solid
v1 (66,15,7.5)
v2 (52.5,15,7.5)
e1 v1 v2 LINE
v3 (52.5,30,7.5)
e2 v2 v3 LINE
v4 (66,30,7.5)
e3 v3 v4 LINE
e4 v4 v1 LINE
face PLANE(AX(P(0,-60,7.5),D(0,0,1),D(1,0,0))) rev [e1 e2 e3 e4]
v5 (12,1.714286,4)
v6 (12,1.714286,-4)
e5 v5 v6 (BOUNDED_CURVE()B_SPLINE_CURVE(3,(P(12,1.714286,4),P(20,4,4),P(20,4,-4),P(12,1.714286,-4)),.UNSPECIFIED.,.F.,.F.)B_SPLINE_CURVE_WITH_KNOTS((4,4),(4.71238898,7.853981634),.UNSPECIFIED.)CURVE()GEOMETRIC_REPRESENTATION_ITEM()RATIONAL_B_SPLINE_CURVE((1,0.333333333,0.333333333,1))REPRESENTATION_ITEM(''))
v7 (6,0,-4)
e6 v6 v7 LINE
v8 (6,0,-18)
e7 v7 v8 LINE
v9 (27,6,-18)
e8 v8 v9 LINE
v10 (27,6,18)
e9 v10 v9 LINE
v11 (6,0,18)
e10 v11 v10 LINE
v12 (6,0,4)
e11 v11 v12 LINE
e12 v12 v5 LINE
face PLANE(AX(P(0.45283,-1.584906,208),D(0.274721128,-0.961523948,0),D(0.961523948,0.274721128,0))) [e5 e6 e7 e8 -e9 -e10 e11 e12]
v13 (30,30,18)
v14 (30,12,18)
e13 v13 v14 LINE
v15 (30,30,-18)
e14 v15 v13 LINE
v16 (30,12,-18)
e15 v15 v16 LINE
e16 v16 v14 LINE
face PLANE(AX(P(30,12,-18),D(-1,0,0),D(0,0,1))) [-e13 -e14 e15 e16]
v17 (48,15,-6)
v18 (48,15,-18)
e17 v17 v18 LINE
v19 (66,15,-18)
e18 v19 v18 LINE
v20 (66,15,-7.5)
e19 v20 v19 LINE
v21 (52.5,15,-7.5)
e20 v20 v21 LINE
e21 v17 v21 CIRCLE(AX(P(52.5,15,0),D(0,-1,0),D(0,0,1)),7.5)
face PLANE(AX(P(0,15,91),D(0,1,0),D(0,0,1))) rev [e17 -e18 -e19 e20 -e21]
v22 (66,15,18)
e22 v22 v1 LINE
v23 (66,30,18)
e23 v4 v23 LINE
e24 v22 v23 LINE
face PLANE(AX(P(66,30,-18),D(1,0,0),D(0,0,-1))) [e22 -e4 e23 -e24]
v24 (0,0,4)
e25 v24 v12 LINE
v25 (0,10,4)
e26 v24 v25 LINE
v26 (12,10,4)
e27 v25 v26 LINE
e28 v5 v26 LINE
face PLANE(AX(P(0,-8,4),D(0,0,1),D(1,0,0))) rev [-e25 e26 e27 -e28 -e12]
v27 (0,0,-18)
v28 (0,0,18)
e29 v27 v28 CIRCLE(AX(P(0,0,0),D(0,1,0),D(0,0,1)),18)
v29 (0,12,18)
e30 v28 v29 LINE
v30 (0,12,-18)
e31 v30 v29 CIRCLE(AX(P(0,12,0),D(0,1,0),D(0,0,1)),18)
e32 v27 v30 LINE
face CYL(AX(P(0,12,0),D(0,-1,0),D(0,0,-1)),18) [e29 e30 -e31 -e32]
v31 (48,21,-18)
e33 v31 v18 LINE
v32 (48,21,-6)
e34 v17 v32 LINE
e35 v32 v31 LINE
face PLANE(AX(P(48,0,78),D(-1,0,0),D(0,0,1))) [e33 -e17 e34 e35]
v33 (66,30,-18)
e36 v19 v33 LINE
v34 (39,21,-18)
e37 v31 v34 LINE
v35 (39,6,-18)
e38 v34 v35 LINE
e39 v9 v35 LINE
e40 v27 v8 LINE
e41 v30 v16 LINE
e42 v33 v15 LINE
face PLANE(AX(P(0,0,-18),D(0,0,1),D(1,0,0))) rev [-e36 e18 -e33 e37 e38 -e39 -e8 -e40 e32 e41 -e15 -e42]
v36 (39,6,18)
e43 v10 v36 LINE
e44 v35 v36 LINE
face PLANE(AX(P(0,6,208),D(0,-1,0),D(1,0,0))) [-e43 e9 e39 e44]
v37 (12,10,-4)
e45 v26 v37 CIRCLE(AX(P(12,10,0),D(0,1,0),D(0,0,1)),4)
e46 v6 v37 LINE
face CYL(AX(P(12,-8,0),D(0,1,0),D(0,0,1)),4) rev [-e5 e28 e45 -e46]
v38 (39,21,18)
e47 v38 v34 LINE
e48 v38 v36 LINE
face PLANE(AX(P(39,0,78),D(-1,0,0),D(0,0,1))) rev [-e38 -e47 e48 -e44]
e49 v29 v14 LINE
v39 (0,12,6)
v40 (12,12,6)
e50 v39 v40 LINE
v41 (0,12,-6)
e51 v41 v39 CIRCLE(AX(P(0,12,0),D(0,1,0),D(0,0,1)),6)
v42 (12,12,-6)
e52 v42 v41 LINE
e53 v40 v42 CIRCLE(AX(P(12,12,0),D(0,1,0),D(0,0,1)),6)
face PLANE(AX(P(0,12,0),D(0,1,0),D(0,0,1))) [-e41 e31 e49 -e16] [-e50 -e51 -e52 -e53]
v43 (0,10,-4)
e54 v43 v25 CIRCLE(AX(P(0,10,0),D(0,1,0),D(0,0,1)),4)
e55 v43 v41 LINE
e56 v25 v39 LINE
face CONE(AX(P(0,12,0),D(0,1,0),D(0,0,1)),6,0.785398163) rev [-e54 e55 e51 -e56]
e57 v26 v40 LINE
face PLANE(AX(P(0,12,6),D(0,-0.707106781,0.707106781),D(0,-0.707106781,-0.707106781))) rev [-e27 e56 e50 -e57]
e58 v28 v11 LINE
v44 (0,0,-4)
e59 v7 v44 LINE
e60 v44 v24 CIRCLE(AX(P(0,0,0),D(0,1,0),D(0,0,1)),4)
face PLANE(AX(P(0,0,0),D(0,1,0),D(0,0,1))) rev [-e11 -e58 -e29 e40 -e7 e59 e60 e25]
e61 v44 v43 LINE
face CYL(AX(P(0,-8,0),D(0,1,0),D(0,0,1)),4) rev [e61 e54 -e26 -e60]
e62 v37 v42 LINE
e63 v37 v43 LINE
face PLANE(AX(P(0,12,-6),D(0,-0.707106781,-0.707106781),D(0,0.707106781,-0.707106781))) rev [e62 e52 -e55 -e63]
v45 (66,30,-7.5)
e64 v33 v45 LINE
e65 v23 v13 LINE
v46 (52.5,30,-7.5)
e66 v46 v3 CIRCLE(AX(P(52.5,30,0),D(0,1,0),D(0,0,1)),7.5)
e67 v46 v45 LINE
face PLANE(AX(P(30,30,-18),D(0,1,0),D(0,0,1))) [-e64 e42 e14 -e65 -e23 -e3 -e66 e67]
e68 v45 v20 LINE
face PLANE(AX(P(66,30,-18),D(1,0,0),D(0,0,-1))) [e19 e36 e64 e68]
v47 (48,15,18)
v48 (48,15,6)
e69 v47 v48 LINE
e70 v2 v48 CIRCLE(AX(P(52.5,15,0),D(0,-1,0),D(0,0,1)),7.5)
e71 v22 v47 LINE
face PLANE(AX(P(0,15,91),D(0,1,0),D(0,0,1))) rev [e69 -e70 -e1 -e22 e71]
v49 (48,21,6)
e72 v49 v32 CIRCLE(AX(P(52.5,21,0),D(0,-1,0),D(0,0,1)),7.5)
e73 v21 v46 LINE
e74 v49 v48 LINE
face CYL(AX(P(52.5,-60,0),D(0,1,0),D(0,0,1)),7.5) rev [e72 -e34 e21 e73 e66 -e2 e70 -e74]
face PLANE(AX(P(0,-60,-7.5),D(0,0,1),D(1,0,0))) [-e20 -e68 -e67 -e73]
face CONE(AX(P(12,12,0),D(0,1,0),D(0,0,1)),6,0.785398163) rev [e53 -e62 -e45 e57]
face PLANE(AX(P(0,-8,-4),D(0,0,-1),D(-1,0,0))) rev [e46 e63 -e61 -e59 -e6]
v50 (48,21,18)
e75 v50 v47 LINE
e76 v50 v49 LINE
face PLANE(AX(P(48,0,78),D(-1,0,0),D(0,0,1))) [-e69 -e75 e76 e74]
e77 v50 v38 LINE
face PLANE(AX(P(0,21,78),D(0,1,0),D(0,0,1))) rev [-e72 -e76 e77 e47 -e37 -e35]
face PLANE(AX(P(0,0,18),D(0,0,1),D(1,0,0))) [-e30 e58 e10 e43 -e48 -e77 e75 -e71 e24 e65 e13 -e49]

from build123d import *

# Parameters (mm, degrees)
HUB_SKETCH_R                = 18
HUB_36_DEPTH                = 12
ARM_START                   = -12
ARM_DEPTH                   = 12
HUB_SLOT_CHAMFER_45_DEPTH   = 2
HUB_SLOT_CHAMFER_45_DRAFT   = -45
HUB_SLOT_DEPTH              = 18
CLEVIS_BLOCK_DEPTH          = 36
CLEVIS_U_SLOT_SKETCH_W      = 13.5
CLEVIS_U_SLOT_SKETCH_H      = 15
CLEVIS_U_SLOT_DEPTH         = 90
BLOCK_STEP_CUT_DEPTH        = 60
BLOCK_STEP_CUT_DEPTH_BACK   = 147
BLOCK_STEP_CUT_SKETCH_W     = 9
BLOCK_STEP_CUT_SKETCH_H     = 21
ARM_TAPER_CUT_DEPTH         = 73
ARM_TAPER_CUT_DEPTH_BACK    = 190
ARM_TAPER_CUT_SKETCH_W      = 18
ARM_TAPER_CUT_SKETCH_H      = 15
BLOCK_RELIEF_CUT_DEPTH      = 190
BLOCK_RELIEF_CUT_DEPTH_BACK = 190


with BuildPart() as part:
    # Hub Sketch → Hub _36 (new body)
    with BuildSketch(Plane(origin=(0, 0, 0), x_dir=(1, 0, 0), z_dir=(0, 1, 0))):
        with Locations(Location((0, 0, 0), (0, 0, 270))):
            Circle(HUB_SKETCH_R)
    extrude(amount=HUB_36_DEPTH)

    # Arm Sketch → Arm (add)
    with BuildSketch(Plane(origin=(0, 12, 0), x_dir=(1, 0, 0), z_dir=(0, 1, 0)).offset(ARM_START)):
        with BuildLine():
            Line((30, 0), (18, 0))
            ThreePointArc((18, 0), (12.727922061, -12.727922061), (0, -18))
            Line((0, -18), (30, -18))
            Line((30, -18), (30, 0))
        make_face()
        with BuildLine():
            ThreePointArc((0, 18), (12.727922061, 12.727922061), (18, 0))
            Line((18, 0), (30, 0))
            Line((30, 0), (30, 18))
            Line((30, 18), (0, 18))
        make_face()
    extrude(amount=ARM_DEPTH)


with BuildPart() as hub_slot_chamfer_45_tool:
    # Hub Slot Chamfer Sketch → Hub Slot Chamfer 45 (with draft: the straight prism first)
    with BuildSketch(Plane(origin=(0, 12, 0), x_dir=(1, 0, 0), z_dir=(0, 1, 0))):
        with BuildLine():
            ThreePointArc((0, 6), (-6, 0), (0, -6))
            Line((0, -6), (12, -6))
            ThreePointArc((12, -6), (18, 0), (12, 6))
            Line((12, 6), (0, 6))
        make_face()
    extrude(amount=-HUB_SLOT_CHAMFER_45_DEPTH)
    # Hub Slot Chamfer 45: the draft: its side faces are tilted about the plane it starts from
    hub_slot_chamfer_45_sides = [hub_slot_chamfer_45_tool.faces().sort_by_distance(p)[0] for p in [
        (6, 11, -6),
        (-6, 11, 0),
        (6, 11, 6),
        (18, 11, 0),
    ]]
    draft(hub_slot_chamfer_45_sides, Plane(origin=(0, 12, 0), x_dir=(1, 0, 0), z_dir=(0, 1, 0)), HUB_SLOT_CHAMFER_45_DRAFT)


with BuildPart() as part_1:
    add(part.part)

    # Hub Slot Chamfer 45: cut by hub_slot_chamfer_45_tool
    add(hub_slot_chamfer_45_tool.part, mode=Mode.SUBTRACT)

    # Hub Slot Sketch → Hub Slot (cut)
    with BuildSketch(Plane(origin=(0, 10, 0), x_dir=(1, 0, 0), z_dir=(0, 1, 0))):
        with BuildLine():
            Line((12, 4), (0, 4))
            ThreePointArc((0, 4), (2.828427125, 2.828427125), (4, 0))
            ThreePointArc((4, 0), (2.828427125, -2.828427125), (0, -4))
            Line((0, -4), (12, -4))
            ThreePointArc((12, -4), (8, 0), (12, 4))
        make_face()
        with BuildLine():
            ThreePointArc((4, 0), (2.828427125, 2.828427125), (0, 4))
            ThreePointArc((0, 4), (-4, 0), (0, -4))
            ThreePointArc((0, -4), (2.828427125, -2.828427125), (4, 0))
        make_face()
        with BuildLine():
            ThreePointArc((16, 0), (14.828427125, 2.828427125), (12, 4))
            ThreePointArc((12, 4), (8, 0), (12, -4))
            ThreePointArc((12, -4), (14.828427125, -2.828427125), (16, 0))
        make_face()
    extrude(amount=-HUB_SLOT_DEPTH, mode=Mode.SUBTRACT)

    # Clevis Block Sketch → Clevis Block (add)
    with BuildSketch(Plane.XY.offset(18)):
        Polygon((30, 12), (30, 30), (66, 30), (66, 15), (66, 0), (30, 0), align=None)
    extrude(amount=-CLEVIS_BLOCK_DEPTH)

    # Clevis U-Slot Sketch → Clevis U-Slot (cut)
    with BuildSketch(Plane(origin=(0, 30, 0), x_dir=(1, 0, 0), z_dir=(0, 1, 0))):
        with BuildLine():
            Line((52.5, -7.5), (52.5, 7.5))
            ThreePointArc((52.5, 7.5), (45, 0), (52.5, -7.5))
        make_face()
        with Locations((59.25, 0)):
            Rectangle(CLEVIS_U_SLOT_SKETCH_W, CLEVIS_U_SLOT_SKETCH_H)
    extrude(amount=-CLEVIS_U_SLOT_DEPTH, mode=Mode.SUBTRACT)

    # Block Step Cut Sketch → Block Step Cut (cut, two sides: drawn at the far end of the back side and taken through both)
    with BuildSketch(Plane.XY.offset(18).offset(-BLOCK_STEP_CUT_DEPTH_BACK)):
        with Locations((43.5, 10.5)):
            Rectangle(BLOCK_STEP_CUT_SKETCH_W, BLOCK_STEP_CUT_SKETCH_H)
    extrude(amount=BLOCK_STEP_CUT_DEPTH + BLOCK_STEP_CUT_DEPTH_BACK, mode=Mode.SUBTRACT)

    # Arm Taper Cut Sketch → Arm Taper Cut (cut, two sides: drawn at the far end of the back side and taken through both)
    with BuildSketch(Plane.XY.offset(18).offset(-ARM_TAPER_CUT_DEPTH_BACK)):
        with Locations((57, 7.5)):
            Rectangle(ARM_TAPER_CUT_SKETCH_W, ARM_TAPER_CUT_SKETCH_H)
    extrude(amount=ARM_TAPER_CUT_DEPTH + ARM_TAPER_CUT_DEPTH_BACK, mode=Mode.SUBTRACT)

    # Block Relief Cut Sketch → Block Relief Cut (cut, two sides: drawn at the far end of the back side and taken through both)
    with BuildSketch(Plane.XY.offset(18).offset(-BLOCK_RELIEF_CUT_DEPTH_BACK)):
        Polygon((39, 0), (39, 6), (27, 6), (6, 0), align=None)
    extrude(amount=BLOCK_RELIEF_CUT_DEPTH + BLOCK_RELIEF_CUT_DEPTH_BACK, mode=Mode.SUBTRACT)


solid = part_1.part
